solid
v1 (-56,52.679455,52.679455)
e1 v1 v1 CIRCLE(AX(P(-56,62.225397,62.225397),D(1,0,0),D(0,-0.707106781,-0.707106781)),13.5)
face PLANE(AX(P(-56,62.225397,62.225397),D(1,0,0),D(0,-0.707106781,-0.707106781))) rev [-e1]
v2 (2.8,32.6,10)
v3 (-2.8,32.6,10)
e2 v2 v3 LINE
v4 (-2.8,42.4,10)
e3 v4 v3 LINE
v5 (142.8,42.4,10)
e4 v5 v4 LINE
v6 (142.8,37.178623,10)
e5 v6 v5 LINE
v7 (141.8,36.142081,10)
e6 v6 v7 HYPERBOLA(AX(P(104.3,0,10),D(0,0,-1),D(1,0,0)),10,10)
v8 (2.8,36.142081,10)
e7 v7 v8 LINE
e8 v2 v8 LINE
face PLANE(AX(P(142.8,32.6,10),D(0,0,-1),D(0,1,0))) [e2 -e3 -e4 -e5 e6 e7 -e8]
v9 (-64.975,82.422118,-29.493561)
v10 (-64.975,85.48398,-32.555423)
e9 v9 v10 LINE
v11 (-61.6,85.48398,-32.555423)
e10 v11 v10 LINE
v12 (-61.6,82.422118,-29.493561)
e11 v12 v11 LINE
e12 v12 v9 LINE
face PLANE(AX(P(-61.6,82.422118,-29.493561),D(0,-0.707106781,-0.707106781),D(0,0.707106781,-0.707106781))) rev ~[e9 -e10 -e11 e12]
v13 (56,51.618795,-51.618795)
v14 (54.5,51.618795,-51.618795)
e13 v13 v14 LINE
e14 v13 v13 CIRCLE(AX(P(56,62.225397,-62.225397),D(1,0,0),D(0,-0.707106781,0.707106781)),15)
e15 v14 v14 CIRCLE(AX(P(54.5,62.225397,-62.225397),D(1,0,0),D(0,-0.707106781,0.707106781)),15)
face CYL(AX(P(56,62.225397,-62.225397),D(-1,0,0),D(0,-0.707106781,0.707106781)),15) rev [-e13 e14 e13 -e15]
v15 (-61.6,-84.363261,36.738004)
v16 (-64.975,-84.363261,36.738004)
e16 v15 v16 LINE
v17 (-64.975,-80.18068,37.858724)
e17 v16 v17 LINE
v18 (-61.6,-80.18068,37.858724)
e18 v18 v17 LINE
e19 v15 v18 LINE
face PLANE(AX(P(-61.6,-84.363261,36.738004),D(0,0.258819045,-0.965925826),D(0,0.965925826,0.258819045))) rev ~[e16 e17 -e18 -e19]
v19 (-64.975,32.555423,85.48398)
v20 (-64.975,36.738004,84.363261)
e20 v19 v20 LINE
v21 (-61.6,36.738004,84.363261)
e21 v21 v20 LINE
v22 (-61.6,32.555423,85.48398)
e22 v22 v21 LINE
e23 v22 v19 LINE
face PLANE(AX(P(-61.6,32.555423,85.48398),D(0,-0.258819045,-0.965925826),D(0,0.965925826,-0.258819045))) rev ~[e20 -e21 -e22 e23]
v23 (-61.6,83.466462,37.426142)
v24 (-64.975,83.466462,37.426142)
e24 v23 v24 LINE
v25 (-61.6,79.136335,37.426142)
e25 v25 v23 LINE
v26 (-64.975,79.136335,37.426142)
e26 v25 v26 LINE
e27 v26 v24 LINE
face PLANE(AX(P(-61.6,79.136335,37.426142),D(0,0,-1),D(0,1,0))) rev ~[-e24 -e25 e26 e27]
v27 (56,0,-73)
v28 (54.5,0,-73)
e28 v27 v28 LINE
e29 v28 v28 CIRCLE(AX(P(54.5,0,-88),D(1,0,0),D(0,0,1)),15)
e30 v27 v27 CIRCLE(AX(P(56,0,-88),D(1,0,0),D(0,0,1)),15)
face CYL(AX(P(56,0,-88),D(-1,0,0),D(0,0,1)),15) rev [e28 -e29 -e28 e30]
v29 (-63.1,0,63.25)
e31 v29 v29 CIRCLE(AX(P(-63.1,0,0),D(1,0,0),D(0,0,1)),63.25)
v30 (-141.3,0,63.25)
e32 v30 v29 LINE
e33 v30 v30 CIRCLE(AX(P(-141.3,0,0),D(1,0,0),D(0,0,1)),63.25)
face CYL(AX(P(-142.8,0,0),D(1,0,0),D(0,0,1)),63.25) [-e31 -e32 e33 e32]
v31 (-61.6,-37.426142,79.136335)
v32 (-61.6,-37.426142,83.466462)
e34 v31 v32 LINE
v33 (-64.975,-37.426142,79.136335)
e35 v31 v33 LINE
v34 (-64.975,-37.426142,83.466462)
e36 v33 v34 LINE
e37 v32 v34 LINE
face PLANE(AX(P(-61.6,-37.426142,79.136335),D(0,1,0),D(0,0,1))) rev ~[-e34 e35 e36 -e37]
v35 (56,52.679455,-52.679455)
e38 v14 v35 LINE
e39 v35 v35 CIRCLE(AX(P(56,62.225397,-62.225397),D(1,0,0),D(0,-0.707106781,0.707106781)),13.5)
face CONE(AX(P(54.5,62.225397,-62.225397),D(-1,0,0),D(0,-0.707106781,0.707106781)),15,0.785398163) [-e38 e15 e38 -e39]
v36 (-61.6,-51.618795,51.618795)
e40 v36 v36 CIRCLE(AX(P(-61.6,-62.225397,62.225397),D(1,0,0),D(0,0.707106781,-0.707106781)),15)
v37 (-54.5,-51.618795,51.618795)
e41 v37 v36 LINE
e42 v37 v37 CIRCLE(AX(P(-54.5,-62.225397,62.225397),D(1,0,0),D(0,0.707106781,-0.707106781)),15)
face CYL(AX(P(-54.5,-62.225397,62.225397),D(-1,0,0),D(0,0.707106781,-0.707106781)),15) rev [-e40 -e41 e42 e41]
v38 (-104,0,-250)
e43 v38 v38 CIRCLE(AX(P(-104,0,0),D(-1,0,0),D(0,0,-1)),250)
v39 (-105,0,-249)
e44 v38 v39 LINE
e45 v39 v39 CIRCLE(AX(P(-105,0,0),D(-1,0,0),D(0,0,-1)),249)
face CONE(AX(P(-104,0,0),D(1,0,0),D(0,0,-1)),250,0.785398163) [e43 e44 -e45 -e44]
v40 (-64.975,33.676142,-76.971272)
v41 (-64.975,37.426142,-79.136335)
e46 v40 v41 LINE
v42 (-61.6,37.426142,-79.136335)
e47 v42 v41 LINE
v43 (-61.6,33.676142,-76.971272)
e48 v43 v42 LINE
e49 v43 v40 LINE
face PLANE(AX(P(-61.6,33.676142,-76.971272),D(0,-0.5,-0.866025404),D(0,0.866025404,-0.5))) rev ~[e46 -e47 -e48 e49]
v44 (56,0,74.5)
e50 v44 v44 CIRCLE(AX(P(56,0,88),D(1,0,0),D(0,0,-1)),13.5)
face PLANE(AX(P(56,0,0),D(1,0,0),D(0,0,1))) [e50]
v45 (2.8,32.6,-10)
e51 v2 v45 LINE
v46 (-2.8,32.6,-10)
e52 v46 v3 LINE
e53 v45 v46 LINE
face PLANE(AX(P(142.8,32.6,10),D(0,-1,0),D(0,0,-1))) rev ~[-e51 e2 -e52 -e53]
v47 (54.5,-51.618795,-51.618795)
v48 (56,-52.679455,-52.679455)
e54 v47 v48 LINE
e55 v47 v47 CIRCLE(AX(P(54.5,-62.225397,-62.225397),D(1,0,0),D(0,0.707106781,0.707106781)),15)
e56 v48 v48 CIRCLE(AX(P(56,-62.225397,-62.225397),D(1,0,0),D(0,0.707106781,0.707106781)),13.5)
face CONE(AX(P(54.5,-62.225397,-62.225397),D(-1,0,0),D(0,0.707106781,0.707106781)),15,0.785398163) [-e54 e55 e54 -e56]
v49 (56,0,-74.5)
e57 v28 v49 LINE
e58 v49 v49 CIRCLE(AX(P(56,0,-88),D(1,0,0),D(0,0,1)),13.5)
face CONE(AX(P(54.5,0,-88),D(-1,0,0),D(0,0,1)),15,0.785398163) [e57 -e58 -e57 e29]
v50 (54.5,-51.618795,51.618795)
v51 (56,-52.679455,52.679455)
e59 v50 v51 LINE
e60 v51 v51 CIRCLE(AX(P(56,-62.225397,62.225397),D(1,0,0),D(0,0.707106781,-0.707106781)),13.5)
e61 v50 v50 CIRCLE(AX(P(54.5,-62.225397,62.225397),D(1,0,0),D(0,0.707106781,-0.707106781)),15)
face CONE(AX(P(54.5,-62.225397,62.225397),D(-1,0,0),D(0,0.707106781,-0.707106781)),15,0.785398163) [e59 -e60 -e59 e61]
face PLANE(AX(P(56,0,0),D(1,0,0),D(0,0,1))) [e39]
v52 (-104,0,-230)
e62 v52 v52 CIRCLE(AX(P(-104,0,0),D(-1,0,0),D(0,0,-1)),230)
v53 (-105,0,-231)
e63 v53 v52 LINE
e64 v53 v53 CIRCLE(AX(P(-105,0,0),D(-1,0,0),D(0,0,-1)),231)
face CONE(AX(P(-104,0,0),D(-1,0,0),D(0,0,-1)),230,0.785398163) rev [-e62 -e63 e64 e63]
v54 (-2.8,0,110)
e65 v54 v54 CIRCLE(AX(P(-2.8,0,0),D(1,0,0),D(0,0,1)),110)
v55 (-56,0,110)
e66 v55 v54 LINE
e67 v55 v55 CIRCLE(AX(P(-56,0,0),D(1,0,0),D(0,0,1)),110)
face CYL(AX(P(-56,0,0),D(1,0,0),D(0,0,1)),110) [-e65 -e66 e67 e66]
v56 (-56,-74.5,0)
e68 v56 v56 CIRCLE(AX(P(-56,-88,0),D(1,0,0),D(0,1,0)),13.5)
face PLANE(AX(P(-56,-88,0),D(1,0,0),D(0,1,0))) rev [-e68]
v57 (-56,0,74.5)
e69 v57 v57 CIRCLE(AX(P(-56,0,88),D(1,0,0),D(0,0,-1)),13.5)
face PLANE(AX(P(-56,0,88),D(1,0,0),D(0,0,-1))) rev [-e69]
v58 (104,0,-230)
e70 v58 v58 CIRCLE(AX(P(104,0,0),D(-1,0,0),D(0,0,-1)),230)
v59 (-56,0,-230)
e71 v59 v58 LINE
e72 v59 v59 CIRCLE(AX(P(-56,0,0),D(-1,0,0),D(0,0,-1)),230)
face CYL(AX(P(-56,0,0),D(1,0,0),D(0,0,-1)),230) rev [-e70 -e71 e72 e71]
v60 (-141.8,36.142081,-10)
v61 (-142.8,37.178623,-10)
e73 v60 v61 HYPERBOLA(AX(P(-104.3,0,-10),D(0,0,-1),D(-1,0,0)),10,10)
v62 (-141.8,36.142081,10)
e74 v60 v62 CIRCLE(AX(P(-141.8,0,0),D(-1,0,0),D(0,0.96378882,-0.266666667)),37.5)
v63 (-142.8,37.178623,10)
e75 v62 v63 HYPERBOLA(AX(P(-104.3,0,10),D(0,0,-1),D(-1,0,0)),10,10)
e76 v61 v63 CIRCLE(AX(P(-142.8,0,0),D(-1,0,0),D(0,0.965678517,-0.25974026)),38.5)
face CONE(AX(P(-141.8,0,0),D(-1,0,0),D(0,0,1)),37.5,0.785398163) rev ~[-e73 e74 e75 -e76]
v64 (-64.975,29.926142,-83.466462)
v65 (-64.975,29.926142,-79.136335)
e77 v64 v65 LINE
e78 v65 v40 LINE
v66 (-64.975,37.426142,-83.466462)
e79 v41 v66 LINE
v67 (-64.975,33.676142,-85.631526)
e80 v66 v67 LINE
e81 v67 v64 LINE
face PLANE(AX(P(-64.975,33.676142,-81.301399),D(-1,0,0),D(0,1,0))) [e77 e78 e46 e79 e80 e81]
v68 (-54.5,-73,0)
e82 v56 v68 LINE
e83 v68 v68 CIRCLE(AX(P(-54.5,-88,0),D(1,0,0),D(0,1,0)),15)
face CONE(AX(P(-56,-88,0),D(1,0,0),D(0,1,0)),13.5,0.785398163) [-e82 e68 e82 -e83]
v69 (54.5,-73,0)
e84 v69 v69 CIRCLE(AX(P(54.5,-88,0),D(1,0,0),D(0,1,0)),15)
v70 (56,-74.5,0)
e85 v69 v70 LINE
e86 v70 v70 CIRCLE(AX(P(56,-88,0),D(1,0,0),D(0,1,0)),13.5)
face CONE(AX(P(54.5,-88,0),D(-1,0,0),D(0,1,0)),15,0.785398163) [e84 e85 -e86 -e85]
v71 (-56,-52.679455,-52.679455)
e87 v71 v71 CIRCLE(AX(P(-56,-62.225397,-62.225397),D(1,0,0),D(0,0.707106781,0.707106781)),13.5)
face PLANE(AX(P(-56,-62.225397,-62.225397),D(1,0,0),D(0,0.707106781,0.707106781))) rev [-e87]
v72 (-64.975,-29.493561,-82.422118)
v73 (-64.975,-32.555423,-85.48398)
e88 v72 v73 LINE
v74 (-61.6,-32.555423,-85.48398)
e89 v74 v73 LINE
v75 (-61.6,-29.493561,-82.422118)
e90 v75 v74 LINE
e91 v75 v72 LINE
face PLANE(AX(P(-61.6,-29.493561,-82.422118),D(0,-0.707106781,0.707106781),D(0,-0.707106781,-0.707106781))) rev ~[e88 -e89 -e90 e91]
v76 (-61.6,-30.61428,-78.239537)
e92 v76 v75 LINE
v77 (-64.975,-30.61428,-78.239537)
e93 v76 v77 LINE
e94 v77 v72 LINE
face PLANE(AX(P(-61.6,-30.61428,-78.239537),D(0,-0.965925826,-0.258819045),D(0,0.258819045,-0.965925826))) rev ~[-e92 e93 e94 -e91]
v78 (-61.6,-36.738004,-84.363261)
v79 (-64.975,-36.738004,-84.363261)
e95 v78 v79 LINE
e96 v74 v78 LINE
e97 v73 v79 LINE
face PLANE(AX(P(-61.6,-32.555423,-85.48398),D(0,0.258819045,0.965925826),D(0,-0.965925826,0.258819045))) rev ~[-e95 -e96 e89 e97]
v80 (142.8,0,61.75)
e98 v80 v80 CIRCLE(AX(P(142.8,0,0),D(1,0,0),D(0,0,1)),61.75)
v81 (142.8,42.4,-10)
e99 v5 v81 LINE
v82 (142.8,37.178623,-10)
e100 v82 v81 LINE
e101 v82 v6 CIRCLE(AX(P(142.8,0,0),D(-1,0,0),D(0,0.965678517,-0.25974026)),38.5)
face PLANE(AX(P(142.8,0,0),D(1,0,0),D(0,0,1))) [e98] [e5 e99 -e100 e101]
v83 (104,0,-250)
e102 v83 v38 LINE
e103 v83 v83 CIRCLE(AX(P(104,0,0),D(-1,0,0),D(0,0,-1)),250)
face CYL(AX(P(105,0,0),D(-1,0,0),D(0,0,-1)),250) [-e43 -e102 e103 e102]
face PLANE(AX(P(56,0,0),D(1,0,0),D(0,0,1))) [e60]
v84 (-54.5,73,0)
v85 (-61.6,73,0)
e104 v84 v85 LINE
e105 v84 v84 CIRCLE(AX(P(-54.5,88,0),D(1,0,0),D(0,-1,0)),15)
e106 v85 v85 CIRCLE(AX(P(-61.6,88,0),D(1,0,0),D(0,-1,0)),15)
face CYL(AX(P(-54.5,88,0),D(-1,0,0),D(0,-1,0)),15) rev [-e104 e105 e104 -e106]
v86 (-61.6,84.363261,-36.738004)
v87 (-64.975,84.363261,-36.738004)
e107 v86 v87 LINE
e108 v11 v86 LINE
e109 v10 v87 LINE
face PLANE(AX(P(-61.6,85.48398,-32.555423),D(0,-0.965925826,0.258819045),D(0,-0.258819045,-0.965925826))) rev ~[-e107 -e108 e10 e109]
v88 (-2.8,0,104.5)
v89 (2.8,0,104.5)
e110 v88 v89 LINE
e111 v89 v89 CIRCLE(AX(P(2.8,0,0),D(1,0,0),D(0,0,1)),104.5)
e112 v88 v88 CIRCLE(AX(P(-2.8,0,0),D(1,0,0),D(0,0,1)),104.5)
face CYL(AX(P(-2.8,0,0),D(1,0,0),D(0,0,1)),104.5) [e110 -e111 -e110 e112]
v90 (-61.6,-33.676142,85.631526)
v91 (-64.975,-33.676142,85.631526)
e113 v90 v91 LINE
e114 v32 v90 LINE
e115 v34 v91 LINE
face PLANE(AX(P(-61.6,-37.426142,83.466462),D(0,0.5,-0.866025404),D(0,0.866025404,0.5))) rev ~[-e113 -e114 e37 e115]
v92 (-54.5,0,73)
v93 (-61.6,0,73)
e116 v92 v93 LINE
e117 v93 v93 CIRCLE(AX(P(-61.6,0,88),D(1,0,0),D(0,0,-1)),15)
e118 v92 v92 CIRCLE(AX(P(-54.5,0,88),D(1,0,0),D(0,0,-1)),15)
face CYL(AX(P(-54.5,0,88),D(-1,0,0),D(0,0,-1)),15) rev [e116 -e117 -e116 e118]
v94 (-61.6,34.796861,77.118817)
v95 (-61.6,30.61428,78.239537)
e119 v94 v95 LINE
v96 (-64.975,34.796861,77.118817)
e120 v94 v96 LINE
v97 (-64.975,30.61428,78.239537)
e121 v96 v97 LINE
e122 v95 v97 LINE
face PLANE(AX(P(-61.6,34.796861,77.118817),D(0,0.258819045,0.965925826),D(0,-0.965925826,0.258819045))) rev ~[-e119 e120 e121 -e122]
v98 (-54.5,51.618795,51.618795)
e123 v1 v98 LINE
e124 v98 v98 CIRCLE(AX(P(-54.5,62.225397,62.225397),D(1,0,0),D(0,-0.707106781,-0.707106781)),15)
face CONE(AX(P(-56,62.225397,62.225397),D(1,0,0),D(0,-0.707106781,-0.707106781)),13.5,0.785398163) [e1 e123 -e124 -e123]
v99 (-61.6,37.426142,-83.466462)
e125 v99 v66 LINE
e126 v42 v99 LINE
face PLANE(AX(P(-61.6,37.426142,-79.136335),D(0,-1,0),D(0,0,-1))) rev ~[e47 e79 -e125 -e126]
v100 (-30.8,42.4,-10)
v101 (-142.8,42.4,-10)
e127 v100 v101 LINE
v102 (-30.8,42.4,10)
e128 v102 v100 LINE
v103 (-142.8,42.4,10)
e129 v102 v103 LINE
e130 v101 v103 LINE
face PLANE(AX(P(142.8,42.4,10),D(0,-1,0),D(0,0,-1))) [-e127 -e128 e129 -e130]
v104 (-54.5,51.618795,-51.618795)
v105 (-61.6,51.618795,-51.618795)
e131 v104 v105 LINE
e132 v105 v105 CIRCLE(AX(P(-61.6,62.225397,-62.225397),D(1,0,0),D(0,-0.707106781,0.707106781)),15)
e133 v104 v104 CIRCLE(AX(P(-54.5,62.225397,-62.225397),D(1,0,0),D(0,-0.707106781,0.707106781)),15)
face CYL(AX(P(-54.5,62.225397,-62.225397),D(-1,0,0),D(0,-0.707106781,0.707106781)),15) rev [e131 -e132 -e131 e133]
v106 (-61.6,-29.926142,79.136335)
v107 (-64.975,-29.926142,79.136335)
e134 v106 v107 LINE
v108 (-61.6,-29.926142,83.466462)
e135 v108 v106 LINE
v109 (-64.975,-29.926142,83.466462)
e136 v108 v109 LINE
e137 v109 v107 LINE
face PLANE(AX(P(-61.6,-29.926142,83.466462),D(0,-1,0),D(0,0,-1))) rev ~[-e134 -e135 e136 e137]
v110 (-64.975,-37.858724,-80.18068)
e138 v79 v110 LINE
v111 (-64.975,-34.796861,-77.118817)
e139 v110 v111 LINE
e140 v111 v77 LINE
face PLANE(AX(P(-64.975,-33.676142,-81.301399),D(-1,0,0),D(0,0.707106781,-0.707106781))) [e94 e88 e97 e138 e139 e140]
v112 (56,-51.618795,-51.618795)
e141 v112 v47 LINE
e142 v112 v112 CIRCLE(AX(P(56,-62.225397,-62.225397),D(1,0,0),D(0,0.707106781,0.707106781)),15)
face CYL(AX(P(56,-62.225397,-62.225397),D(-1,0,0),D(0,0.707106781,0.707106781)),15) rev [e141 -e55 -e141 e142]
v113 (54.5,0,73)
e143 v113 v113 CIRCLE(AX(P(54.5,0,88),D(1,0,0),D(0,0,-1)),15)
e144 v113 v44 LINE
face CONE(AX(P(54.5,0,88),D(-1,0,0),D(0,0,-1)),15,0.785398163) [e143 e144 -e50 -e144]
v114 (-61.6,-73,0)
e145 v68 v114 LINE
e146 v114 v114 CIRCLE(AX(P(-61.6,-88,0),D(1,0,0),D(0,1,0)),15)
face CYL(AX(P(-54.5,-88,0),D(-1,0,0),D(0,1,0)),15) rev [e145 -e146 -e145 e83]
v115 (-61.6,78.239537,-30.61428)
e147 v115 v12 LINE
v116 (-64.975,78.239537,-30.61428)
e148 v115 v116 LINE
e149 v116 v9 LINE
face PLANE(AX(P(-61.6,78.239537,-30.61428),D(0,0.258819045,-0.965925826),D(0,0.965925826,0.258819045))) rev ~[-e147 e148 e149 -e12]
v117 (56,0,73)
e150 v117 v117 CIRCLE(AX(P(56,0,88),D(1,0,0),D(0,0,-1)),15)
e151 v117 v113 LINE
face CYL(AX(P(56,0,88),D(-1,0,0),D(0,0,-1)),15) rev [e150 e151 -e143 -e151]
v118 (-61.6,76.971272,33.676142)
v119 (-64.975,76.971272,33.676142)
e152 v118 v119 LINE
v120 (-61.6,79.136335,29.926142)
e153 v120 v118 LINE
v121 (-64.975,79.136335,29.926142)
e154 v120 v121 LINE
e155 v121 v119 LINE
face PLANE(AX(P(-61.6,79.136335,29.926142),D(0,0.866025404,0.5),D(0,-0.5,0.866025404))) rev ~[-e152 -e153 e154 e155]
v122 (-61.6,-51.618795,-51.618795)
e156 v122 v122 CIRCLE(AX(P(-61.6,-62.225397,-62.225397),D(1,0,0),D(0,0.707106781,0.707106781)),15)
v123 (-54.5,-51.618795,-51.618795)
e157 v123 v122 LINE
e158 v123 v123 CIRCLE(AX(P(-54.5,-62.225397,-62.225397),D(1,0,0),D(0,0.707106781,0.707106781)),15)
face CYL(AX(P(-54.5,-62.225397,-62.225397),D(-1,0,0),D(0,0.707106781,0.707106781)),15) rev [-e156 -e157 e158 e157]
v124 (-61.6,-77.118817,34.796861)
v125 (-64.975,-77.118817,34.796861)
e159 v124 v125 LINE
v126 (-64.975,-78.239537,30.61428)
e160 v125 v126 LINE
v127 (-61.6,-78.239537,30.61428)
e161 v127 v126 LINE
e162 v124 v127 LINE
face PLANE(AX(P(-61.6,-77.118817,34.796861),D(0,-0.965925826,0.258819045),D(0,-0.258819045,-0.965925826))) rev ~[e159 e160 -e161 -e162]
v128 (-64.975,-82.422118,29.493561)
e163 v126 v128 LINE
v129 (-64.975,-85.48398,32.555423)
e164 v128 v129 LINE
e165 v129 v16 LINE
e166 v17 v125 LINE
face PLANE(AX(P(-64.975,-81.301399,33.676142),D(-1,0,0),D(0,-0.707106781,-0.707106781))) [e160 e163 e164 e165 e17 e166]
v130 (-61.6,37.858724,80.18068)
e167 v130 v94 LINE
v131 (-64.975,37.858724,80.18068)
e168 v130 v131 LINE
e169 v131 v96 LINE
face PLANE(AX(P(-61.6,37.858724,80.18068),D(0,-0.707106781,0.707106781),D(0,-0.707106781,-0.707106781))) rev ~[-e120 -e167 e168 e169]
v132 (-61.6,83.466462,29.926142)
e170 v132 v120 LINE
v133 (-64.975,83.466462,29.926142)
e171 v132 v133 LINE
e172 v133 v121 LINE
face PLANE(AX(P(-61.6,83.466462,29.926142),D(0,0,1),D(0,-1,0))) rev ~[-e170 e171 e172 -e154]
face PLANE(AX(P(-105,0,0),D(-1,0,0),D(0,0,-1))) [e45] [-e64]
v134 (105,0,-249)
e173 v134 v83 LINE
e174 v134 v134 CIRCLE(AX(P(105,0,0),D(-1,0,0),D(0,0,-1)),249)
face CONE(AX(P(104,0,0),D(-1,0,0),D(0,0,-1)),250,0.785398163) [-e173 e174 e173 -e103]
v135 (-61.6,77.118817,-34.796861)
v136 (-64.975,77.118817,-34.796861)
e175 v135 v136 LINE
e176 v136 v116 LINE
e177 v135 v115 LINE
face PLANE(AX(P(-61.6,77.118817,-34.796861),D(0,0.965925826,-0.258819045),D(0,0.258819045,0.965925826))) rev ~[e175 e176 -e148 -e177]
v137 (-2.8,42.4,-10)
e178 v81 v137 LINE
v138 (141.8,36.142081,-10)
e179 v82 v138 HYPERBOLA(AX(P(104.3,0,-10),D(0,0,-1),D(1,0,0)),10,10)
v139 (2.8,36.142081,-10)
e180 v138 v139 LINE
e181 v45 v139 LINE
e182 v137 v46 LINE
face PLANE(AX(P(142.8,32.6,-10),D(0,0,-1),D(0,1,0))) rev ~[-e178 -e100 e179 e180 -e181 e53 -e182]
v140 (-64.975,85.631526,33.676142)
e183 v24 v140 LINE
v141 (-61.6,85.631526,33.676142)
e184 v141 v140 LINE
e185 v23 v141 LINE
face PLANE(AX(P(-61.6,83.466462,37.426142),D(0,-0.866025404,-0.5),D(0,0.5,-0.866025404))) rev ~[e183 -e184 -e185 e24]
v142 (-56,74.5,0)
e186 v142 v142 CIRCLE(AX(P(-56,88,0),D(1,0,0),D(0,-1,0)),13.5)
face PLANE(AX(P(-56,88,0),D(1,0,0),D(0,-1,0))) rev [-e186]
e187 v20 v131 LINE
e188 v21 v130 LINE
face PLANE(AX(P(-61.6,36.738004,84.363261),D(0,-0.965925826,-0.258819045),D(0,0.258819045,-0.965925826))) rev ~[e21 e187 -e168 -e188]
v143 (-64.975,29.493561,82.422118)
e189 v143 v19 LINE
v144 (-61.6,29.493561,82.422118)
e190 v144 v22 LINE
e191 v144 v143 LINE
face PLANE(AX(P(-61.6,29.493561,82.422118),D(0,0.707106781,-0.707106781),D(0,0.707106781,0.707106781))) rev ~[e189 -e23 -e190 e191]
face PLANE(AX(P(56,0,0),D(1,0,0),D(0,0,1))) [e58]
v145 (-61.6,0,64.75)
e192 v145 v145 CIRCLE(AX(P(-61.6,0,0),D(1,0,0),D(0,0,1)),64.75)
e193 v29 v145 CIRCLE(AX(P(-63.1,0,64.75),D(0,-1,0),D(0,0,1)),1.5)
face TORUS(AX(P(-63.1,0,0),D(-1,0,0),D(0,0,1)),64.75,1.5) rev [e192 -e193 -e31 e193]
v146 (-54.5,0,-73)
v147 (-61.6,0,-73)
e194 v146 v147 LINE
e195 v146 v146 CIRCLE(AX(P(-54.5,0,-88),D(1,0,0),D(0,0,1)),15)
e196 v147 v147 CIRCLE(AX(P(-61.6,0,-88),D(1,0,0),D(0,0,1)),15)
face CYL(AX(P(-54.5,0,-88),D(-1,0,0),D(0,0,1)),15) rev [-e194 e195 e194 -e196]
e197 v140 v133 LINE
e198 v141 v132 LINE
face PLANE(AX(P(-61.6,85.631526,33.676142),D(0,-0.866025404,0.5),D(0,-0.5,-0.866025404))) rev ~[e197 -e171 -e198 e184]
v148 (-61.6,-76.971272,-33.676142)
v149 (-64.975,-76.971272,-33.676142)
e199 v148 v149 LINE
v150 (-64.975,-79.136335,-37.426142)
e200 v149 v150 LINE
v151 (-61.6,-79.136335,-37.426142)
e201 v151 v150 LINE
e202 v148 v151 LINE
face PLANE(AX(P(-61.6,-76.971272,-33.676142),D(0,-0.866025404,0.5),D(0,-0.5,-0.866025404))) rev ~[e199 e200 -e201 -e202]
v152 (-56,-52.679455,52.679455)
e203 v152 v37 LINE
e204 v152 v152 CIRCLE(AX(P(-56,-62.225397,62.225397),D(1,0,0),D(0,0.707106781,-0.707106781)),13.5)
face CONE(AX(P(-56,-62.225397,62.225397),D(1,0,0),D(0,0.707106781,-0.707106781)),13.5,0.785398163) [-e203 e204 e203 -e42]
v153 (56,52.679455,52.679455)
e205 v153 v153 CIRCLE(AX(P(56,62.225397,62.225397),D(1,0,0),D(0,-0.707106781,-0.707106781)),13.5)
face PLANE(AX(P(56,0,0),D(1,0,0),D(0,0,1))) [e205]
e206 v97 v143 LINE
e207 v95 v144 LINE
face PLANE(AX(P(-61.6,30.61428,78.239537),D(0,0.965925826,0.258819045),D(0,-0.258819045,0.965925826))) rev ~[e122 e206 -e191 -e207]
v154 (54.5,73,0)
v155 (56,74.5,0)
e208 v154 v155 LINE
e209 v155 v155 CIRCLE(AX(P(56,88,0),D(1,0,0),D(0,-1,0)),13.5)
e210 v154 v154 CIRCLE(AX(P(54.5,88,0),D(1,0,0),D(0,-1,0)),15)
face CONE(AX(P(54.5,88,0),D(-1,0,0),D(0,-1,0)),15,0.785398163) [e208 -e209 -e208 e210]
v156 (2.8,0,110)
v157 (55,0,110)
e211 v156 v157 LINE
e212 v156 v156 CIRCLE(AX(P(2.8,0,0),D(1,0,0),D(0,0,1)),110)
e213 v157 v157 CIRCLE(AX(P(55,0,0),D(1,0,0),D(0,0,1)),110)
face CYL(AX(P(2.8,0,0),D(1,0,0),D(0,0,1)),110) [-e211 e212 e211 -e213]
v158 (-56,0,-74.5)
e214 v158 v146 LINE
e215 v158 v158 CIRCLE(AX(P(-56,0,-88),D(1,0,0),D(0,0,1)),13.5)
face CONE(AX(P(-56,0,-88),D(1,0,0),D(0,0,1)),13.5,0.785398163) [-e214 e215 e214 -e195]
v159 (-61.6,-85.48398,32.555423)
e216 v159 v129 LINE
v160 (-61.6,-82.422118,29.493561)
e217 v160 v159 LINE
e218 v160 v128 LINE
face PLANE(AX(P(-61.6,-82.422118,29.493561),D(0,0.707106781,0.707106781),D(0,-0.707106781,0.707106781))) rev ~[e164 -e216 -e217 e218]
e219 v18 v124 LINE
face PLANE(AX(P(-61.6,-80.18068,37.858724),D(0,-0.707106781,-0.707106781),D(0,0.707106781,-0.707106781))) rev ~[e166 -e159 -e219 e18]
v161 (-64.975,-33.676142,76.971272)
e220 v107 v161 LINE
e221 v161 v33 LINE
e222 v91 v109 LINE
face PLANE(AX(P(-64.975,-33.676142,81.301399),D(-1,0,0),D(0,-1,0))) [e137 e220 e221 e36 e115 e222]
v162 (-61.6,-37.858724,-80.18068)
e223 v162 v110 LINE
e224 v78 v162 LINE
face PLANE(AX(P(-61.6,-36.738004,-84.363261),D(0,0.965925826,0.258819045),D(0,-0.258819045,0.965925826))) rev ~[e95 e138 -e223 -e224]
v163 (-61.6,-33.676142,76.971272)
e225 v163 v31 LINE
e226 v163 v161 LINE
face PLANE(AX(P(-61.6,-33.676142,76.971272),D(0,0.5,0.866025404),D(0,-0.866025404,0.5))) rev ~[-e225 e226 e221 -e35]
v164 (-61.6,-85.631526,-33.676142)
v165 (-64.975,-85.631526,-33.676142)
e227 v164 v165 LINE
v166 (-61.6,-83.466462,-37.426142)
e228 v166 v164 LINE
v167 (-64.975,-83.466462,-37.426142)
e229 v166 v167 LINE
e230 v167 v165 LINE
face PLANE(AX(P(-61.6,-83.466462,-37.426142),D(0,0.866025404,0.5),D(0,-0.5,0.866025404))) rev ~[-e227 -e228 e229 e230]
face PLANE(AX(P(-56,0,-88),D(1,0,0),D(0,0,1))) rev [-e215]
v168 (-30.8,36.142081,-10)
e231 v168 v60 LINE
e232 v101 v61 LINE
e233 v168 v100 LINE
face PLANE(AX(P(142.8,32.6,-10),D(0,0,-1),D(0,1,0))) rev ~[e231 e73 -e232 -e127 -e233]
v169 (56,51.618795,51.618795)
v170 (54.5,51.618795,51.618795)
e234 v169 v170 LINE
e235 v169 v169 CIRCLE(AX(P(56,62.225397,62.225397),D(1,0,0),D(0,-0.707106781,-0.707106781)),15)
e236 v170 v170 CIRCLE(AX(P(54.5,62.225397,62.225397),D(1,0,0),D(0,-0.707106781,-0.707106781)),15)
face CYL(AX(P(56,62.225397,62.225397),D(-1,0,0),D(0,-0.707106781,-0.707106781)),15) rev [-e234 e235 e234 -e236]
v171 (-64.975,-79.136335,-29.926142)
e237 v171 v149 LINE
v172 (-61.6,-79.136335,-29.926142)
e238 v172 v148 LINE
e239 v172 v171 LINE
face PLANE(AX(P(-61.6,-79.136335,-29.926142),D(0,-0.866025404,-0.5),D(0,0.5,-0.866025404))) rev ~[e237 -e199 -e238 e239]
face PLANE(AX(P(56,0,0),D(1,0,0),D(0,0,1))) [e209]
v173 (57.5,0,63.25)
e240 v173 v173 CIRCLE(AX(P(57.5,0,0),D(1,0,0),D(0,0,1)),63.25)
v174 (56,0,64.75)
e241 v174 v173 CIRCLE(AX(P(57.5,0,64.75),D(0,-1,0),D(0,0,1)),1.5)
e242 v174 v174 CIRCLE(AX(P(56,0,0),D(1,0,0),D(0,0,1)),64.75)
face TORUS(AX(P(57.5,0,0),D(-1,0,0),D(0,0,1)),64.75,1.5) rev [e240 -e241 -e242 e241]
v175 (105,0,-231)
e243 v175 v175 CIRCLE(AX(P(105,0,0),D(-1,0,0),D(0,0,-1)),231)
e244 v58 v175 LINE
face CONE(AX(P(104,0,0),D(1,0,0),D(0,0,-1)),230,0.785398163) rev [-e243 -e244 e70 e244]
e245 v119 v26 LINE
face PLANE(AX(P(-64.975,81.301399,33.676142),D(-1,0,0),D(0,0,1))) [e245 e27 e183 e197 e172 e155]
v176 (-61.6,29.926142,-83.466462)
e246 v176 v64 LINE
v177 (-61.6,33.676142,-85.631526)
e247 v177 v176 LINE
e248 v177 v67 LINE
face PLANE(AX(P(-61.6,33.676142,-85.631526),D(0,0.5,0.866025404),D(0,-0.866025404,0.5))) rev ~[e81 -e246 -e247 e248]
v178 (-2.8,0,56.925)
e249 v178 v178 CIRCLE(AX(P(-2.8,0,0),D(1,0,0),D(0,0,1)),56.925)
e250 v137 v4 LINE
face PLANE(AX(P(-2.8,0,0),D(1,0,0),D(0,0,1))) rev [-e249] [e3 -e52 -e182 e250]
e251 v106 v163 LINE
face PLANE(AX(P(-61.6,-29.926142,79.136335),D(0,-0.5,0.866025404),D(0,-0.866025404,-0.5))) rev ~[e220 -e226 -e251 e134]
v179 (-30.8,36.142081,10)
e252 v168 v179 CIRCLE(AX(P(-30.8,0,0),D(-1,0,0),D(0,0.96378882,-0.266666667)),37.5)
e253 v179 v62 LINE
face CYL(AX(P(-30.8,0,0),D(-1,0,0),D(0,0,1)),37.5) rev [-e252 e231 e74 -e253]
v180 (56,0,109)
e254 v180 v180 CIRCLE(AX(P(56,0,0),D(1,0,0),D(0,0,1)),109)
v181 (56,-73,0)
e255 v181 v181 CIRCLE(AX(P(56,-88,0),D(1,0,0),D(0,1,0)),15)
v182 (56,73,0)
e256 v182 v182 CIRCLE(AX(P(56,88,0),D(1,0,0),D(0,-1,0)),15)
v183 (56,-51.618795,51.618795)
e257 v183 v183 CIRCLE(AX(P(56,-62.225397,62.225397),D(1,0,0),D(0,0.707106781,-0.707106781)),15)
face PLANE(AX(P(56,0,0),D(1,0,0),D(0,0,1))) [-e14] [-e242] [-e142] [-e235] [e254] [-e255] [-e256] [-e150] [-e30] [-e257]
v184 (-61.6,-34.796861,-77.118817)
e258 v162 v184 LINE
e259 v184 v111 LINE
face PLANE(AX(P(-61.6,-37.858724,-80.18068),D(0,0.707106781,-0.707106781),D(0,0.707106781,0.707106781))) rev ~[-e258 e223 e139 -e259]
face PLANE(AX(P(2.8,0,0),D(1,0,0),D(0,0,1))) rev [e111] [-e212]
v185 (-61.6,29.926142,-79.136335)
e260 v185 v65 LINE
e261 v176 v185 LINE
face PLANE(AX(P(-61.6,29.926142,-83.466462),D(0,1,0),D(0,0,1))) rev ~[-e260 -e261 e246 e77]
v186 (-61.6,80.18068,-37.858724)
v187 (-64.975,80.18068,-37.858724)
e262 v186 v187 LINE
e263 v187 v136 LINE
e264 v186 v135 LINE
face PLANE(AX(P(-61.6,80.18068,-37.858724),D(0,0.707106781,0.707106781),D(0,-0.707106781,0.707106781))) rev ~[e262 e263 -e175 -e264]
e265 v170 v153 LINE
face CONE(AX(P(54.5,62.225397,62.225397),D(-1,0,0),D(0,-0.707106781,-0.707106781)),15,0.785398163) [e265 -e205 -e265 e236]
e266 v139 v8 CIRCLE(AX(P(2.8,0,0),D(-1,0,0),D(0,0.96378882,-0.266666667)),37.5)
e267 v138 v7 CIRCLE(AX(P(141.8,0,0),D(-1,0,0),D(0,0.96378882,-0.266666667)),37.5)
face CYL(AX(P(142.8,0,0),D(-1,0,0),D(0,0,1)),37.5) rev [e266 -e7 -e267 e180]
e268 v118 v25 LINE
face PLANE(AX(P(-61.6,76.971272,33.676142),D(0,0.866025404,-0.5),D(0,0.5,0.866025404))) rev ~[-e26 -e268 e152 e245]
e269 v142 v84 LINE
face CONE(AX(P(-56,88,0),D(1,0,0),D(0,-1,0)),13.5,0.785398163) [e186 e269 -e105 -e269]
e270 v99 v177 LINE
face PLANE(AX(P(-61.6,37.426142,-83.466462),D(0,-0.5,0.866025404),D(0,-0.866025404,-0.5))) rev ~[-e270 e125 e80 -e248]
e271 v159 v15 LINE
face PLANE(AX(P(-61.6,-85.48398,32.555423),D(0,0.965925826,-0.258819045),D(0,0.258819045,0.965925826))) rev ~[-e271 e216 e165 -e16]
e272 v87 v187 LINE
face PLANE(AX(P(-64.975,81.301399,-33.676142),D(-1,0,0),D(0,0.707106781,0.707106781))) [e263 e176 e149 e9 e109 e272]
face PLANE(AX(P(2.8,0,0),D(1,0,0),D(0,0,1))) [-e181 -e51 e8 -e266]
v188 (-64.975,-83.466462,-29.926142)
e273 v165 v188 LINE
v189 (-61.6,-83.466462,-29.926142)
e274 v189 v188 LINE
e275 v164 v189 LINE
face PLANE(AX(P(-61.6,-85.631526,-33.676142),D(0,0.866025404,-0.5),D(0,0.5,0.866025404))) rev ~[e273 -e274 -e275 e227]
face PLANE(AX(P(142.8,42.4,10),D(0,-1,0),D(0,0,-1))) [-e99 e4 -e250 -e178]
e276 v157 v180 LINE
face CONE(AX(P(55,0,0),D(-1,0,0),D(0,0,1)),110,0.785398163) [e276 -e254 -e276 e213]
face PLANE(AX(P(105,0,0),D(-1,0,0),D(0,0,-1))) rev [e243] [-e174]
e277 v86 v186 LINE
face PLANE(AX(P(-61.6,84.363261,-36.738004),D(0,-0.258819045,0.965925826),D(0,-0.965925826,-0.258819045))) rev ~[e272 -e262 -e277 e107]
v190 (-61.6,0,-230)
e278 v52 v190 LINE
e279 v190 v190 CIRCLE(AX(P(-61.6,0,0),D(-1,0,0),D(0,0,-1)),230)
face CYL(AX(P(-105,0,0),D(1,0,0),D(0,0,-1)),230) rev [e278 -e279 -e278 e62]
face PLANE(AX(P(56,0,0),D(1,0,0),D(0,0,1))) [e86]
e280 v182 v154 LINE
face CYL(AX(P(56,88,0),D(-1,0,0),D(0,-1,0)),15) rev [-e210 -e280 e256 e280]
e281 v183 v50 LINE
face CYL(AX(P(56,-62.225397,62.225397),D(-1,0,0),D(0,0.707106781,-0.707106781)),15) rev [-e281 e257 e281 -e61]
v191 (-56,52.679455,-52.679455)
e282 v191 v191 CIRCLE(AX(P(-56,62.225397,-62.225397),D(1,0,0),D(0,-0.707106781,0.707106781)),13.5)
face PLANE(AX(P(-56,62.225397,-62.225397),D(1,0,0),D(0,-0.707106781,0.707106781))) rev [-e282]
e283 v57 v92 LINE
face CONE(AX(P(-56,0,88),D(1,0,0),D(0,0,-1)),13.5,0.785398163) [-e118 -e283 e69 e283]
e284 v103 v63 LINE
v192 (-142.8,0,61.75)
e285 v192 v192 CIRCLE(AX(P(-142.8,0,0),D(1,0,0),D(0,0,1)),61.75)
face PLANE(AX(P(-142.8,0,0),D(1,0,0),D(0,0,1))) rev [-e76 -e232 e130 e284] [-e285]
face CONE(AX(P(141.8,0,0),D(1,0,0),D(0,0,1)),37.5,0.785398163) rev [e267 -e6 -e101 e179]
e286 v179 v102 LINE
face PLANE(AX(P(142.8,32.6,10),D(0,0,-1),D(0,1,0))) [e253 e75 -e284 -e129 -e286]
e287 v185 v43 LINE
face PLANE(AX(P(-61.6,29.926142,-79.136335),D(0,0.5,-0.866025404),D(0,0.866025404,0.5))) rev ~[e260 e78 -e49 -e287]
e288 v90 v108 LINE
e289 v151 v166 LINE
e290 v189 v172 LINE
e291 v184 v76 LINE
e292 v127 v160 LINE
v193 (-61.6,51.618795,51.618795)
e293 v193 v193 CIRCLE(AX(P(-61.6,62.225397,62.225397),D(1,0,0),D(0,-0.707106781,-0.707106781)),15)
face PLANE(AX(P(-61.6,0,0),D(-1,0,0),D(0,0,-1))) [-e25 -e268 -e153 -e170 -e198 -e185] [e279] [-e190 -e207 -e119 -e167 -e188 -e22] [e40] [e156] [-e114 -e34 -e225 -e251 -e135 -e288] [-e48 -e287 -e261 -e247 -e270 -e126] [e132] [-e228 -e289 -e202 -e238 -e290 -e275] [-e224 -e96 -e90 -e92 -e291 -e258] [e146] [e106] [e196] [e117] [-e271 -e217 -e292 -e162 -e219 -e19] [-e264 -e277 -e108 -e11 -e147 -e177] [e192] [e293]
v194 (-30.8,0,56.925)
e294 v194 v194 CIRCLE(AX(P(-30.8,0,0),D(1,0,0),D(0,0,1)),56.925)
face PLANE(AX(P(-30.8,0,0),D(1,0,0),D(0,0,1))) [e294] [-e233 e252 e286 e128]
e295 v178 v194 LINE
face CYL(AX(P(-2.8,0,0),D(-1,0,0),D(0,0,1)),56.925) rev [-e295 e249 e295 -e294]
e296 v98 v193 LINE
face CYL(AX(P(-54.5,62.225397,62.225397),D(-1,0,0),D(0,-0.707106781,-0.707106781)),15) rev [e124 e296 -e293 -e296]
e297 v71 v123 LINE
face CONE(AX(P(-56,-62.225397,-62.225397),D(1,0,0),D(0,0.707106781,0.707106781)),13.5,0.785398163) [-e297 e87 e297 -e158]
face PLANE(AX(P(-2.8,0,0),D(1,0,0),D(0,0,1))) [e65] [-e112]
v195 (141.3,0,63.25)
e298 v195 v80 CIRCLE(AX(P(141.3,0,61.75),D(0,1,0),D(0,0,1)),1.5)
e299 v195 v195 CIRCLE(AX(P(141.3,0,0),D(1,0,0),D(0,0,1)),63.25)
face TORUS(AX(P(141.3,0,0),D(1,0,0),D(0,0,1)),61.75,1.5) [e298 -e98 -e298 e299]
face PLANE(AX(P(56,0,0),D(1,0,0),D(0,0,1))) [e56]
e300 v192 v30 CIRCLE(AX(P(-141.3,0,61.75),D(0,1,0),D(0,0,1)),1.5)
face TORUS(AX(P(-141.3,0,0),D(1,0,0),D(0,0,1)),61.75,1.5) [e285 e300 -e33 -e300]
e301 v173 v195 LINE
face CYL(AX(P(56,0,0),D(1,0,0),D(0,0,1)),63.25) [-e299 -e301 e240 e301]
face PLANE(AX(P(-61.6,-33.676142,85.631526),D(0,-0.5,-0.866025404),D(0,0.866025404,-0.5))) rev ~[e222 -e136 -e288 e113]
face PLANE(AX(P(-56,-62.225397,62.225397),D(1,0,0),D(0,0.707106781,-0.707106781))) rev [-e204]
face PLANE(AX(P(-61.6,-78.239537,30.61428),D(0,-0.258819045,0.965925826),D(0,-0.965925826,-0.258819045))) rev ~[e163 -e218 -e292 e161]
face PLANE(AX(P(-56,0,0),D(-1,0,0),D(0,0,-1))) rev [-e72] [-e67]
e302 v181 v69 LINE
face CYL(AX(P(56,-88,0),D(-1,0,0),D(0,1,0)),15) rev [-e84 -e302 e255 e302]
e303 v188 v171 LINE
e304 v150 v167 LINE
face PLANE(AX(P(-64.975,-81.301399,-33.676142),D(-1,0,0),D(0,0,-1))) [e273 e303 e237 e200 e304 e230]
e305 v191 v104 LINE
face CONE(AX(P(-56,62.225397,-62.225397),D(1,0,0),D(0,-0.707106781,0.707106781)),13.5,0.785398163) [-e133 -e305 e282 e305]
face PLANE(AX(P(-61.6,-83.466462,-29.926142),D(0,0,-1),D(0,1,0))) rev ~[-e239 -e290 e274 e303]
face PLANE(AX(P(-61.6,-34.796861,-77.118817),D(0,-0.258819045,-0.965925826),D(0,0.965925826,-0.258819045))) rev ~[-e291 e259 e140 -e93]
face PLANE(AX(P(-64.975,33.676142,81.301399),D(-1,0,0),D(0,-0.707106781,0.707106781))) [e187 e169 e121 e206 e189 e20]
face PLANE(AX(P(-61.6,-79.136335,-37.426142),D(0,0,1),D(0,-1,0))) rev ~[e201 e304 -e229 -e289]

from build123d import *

# Parameters (mm, degrees)
CHAMFER1_SIZE      = 1
CHAMFER2_SIZE      = 1
CHAMFER3_SIZE      = 1
FILLET1_R          = 1.5
FILLET2_R          = 1.5
EXTRUDE1_DEPTH     = 3.375
CIRPATTERN11_COUNT = 8
SKETCH6_W          = 20
SKETCH6_H          = 9.8
CUT_EXTRUDE1_DEPTH = 455.496820734


with BuildPart() as part:
    # Sketch1 → Revolve1 (revolve)
    with BuildSketch(Plane.XY, mode=Mode.PRIVATE) as revolve1_sk:
        Polygon((-2.8, 56.925), (-30.8, 56.925), (-30.8, 37.5), (-142.8, 37.5), (-142.8, 63.25), (-61.6, 63.25), (-61.6, 68.85), (-56, 68.85), (-56, 110), (-2.8, 110), (-2.8, 104.5), (2.8, 104.5), (2.8, 110), (56, 110), (56, 63.25), (142.8, 63.25), (142.8, 37.5), (2.8, 37.5), (2.8, 0), (-2.8, 0), align=None)
    revolve(revolve1_sk.sketch.rotate(Axis((-114.849033811, 0, 0), (1, 0, 0)), 90), axis=Axis((-114.849033811, 0, 0), (1, 0, 0)))

    # Sketch2 → Revolve2 (revolve)
    with BuildSketch(Plane.XY, mode=Mode.PRIVATE) as revolve2_sk:
        Polygon((105, 250), (-105, 250), (-105, 230), (-61.6, 230), (-61.6, 68.85), (-56, 68.85), (-56, 230), (105, 230), align=None)
    revolve(revolve2_sk.sketch.rotate(Axis((0, 0, 0), (-1, 0, 0)), 90), axis=Axis((0, 0, 0), (-1, 0, 0)))

    # Sketch3 → Cut-Revolve1 (revolve, cut)
    with BuildSketch(Plane.XY, mode=Mode.PRIVATE) as cut_revolve1_sk:
        Polygon((-56, 103), (-61.6, 103), (-61.6, 88), (-56, 88), (-56, 101.5), (-54.5, 103), align=None)
        Polygon((56, 103), (54.5, 103), (56, 101.5), align=None)
    cut_revolve1 = revolve(cut_revolve1_sk.sketch.rotate(Axis((-61.6, 88, 0), (1, 0, 0)), 180), axis=Axis((-61.6, 88, 0), (1, 0, 0)), mode=Mode.SUBTRACT)

    # Chamfer1
    chamfer1_edges = [part.edges().sort_by_distance(p)[0] for p in [
        (142.8, 0, -37.5),
        (56, 0, -110),
    ]]
    chamfer(chamfer1_edges, length=CHAMFER1_SIZE)

    # Chamfer2
    chamfer2_edges = [part.edges().sort_by_distance(p)[0] for p in [
        (105, 0, 250),
        (105, 0, 230),
        (-105, 0, 230),
        (-105, 0, 250),
    ]]
    chamfer(chamfer2_edges, length=CHAMFER2_SIZE)

    # Chamfer3
    chamfer3_edges = [part.edges().sort_by_distance(p)[0] for p in [
        (-142.8, 0, -37.5),
    ]]
    chamfer(chamfer3_edges, length=CHAMFER3_SIZE)

    # Fillet1
    fillet1_edges = [part.edges().sort_by_distance(p)[0] for p in [
        (-61.6, 0, -63.25),
        (-142.8, 0, -63.25),
    ]]
    fillet(fillet1_edges, radius=FILLET1_R)

    # Fillet2
    fillet2_edges = [part.edges().sort_by_distance(p)[0] for p in [
        (142.8, 0, -63.25),
        (56, 0, -63.25),
    ]]
    fillet(fillet2_edges, radius=FILLET2_R)

    # Sketch5 → Extrude1 (add)
    with BuildSketch(Plane.ZY.offset(61.6)):
        Polygon((33.676142048, 76.971271842), (37.426142048, 79.136335352), (37.426142048, 83.46646237), (33.676142048, 85.63152588), (29.926142048, 83.46646237), (29.926142048, 79.136335352), align=None)
    extrude1 = extrude(amount=EXTRUDE1_DEPTH)

    # CirPattern11: Cut-Revolve1, Extrude1 ×8 about axis
    cirpattern11_axis = Axis((0, 0, 0), (1, 0, 0))
    add([cut_revolve1.rotate(cirpattern11_axis, i * 360 / CIRPATTERN11_COUNT) for i in range(1, CIRPATTERN11_COUNT)], mode=Mode.SUBTRACT)
    add([extrude1.rotate(cirpattern11_axis, i * 360 / CIRPATTERN11_COUNT) for i in range(1, CIRPATTERN11_COUNT)])

    # Sketch6 → Cut-Extrude1 (cut, through all)
    with BuildSketch(Plane(origin=(142.8, 0, 0), x_dir=(0, 0, -1), z_dir=(1, 0, 0))):
        with Locations((0, 37.5)):
            Rectangle(SKETCH6_W, SKETCH6_H)
    extrude(amount=-CUT_EXTRUDE1_DEPTH, mode=Mode.SUBTRACT)


solid = part.part
